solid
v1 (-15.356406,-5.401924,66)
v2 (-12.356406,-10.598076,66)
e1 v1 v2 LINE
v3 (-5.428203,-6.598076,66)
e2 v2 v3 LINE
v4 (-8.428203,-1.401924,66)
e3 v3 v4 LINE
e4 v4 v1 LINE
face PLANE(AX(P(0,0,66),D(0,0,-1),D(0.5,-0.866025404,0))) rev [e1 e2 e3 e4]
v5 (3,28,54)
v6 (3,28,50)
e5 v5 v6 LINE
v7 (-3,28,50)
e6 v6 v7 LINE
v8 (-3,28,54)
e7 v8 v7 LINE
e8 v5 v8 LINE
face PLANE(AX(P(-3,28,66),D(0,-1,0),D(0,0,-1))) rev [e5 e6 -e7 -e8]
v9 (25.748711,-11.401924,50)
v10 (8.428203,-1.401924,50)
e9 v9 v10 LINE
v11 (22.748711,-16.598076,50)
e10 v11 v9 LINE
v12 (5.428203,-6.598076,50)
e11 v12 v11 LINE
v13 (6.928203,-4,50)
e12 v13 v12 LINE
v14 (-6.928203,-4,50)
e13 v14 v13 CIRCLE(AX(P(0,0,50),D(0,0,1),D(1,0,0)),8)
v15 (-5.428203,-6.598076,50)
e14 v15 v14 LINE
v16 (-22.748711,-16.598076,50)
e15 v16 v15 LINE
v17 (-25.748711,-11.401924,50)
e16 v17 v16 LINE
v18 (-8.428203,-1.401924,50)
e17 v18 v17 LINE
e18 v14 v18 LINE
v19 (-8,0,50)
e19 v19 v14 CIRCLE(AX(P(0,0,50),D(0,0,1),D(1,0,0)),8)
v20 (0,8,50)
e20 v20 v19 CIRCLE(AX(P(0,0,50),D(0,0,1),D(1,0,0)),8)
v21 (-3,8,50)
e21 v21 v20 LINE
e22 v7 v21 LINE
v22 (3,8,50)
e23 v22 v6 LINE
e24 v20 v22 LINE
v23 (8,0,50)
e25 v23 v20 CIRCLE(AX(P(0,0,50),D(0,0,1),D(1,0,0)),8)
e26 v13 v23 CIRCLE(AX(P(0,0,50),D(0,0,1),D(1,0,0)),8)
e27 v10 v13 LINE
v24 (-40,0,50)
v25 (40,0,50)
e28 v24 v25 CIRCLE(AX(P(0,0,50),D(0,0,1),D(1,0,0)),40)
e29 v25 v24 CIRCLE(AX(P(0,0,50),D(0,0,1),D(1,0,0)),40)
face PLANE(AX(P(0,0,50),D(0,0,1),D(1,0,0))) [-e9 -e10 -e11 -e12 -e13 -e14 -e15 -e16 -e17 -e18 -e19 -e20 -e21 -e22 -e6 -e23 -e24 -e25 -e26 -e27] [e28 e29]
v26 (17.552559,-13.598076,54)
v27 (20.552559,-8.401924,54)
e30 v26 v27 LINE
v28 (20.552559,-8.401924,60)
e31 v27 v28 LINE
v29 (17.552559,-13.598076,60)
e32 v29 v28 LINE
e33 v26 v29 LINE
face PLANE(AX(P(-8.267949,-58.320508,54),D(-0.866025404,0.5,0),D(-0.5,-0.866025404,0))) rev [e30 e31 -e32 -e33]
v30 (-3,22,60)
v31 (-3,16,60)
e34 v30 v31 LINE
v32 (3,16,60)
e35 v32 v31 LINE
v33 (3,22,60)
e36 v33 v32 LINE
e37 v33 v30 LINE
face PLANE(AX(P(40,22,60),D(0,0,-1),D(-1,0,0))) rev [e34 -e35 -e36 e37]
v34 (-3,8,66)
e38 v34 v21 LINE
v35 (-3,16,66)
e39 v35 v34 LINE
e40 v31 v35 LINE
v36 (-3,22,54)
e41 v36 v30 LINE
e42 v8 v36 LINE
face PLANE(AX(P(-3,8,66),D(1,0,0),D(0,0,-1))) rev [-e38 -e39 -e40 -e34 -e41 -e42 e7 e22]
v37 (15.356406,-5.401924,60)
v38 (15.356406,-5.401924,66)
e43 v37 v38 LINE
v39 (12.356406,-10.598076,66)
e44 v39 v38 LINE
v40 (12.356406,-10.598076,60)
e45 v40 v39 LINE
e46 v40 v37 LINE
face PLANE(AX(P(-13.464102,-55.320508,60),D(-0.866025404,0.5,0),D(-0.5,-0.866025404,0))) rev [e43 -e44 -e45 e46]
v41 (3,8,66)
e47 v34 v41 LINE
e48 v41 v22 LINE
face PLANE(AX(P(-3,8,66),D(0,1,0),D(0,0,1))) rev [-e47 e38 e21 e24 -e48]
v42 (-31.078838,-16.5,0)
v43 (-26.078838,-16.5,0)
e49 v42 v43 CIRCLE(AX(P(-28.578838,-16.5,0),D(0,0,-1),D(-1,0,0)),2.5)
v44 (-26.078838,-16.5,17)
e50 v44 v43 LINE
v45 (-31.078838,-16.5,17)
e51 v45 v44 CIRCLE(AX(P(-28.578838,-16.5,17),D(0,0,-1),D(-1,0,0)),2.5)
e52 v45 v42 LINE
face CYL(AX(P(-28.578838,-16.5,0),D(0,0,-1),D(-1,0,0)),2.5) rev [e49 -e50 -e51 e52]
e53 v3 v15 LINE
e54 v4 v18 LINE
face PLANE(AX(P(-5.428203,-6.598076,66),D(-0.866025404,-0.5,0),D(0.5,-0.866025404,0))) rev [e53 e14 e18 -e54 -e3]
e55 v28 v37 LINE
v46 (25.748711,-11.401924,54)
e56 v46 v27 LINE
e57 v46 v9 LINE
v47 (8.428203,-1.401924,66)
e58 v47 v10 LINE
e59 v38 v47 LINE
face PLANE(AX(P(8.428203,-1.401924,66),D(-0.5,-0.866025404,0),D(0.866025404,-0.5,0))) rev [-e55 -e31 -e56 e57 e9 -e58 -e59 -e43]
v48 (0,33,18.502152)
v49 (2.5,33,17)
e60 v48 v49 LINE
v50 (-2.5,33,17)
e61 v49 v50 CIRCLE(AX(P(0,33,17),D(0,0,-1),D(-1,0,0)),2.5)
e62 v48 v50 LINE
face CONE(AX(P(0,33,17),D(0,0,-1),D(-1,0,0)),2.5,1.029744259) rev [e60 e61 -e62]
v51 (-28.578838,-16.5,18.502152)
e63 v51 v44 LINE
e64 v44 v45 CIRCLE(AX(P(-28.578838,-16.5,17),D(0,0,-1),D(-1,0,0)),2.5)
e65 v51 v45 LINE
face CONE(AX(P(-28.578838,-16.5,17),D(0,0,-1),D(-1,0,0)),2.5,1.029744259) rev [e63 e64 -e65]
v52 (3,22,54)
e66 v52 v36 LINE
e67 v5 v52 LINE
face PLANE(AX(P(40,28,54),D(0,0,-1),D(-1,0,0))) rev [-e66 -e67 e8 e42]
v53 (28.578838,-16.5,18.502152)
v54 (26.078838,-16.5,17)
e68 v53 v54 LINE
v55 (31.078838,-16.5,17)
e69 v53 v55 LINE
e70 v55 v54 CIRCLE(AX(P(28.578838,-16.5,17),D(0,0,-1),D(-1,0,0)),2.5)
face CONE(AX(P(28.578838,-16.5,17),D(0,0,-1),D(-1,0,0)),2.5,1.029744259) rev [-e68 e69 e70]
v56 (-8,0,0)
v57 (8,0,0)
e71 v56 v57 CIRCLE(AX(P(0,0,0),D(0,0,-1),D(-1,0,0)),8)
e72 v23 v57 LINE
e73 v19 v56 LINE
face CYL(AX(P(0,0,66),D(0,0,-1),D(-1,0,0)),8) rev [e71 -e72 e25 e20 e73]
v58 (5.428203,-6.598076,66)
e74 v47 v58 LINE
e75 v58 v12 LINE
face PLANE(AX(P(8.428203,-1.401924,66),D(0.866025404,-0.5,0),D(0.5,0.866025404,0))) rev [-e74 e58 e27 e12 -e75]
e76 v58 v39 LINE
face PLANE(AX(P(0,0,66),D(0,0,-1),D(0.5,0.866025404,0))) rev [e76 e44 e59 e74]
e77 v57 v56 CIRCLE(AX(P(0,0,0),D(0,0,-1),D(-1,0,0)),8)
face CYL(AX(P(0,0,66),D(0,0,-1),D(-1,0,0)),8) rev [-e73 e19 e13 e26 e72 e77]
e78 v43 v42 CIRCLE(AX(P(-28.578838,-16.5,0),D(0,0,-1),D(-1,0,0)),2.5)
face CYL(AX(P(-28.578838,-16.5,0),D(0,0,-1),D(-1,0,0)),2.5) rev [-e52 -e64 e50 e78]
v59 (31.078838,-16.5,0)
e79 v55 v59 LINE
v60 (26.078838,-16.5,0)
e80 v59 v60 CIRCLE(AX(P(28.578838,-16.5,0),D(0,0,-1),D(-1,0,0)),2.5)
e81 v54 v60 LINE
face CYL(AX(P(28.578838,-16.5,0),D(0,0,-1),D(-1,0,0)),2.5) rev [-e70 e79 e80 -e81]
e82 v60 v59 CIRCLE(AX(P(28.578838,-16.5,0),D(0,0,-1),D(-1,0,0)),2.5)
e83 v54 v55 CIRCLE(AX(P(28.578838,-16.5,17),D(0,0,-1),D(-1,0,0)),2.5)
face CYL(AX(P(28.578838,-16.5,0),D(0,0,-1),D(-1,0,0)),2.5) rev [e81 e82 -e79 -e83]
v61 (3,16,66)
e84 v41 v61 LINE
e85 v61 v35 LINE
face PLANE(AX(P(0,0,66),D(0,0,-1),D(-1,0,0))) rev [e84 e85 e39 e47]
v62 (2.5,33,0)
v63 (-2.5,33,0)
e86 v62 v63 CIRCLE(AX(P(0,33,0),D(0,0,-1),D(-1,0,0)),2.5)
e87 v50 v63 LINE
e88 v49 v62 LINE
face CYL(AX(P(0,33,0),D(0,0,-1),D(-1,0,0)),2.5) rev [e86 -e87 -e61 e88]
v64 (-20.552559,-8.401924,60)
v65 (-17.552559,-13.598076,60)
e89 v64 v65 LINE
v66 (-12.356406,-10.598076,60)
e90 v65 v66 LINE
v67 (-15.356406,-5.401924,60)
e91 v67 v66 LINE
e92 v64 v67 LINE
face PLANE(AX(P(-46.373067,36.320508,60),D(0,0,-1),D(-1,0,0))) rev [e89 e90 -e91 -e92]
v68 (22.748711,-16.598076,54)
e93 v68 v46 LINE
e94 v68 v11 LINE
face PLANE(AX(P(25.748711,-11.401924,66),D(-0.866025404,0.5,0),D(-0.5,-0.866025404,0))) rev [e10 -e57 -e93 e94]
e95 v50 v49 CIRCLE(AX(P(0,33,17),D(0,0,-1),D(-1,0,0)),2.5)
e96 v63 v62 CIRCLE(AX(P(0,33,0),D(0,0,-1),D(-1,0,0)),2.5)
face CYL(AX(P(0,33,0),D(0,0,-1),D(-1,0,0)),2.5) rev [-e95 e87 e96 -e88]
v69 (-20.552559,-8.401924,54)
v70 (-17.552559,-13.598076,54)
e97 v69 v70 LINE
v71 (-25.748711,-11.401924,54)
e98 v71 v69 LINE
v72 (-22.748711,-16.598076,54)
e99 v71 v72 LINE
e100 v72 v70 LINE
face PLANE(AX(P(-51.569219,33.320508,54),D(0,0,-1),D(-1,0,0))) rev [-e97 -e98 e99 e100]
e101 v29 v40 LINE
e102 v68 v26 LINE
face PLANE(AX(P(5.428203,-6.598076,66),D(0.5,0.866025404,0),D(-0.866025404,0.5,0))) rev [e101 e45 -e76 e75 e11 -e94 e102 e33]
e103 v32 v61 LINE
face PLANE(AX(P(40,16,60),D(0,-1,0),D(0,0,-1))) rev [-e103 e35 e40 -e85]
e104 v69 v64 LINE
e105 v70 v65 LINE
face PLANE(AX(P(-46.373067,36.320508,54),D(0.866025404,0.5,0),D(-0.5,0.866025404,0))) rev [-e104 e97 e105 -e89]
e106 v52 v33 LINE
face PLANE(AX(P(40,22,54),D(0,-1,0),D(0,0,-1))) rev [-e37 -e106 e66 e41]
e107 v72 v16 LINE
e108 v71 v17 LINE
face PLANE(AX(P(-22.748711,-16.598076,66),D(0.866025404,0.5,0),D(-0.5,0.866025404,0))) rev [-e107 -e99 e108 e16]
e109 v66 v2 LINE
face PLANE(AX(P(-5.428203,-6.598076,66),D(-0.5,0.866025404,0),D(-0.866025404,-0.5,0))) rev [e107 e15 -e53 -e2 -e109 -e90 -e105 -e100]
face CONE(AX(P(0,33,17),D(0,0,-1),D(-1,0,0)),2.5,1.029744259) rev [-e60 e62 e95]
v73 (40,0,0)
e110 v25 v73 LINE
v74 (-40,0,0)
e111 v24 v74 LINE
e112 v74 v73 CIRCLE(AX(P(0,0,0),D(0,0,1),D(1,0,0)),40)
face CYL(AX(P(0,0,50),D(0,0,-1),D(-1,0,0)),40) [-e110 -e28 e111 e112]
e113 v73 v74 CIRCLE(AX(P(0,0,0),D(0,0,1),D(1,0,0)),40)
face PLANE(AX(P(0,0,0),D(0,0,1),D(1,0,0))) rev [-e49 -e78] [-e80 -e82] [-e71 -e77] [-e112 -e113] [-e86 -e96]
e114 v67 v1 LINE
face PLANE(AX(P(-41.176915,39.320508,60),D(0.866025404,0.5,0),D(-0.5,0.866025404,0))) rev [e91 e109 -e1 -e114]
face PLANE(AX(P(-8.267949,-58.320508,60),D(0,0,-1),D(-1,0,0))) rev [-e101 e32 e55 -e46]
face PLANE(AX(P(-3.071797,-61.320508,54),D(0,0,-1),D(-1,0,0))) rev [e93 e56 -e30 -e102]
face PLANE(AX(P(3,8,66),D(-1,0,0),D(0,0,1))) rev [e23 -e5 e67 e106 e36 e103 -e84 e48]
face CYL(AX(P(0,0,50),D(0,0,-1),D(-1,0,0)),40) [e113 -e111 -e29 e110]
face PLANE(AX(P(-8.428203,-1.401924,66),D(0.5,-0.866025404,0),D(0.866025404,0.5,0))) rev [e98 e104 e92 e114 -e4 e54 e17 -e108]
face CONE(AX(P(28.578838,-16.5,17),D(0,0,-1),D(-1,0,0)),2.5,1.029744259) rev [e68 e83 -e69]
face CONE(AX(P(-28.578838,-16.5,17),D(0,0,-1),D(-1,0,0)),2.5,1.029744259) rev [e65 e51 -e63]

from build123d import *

# Parameters (mm, degrees)
SKETCH_1_R               = 40
EXTRUDE_1_DEPTH          = 50
SKETCH_2_W               = 6
SKETCH_2_H               = 20
EXTRUDE_2_DEPTH          = 16
CUT_EXTRUDE_1_DEPTH      = 89.345911054
PATTERN_CIRCULAR_1_COUNT = 3
SKETCH_4_R               = 8
CUT_EXTRUDE_2_DEPTH      = 87.925255248
PATTERN_CIRCULAR_2_COUNT = 3


with BuildPart() as part:
    # 草图1 → 凸台-拉伸1 (new body)
    with BuildSketch(Plane.XY):
        Circle(SKETCH_1_R)
    extrude(amount=EXTRUDE_1_DEPTH)

    # 草图2 → 凸台-拉伸2 (add)
    with BuildSketch(Plane.XY.offset(50)):
        with Locations((0, 18)):
            Rectangle(SKETCH_2_W, SKETCH_2_H)
    extrude_2 = extrude(amount=EXTRUDE_2_DEPTH)

    # 草图3 → 切除-拉伸1 (cut, through all)
    with BuildSketch(Plane.ZY.offset(3)):
        Polygon((54, 28), (54, 22), (60, 22), (60, 16), (66, 16), (66, 28), align=None)
    cut_extrude_1 = extrude(amount=-CUT_EXTRUDE_1_DEPTH, mode=Mode.SUBTRACT)

    # 阵列(圆周)1: 凸台-拉伸2, 切除-拉伸1 ×3 about axis
    pattern_circular_1_axis = Axis((0, 0, 0), (0, 0, 1))
    add([extrude_2.rotate(pattern_circular_1_axis, i * 360 / PATTERN_CIRCULAR_1_COUNT) for i in range(1, PATTERN_CIRCULAR_1_COUNT)])
    add([cut_extrude_1.rotate(pattern_circular_1_axis, i * 360 / PATTERN_CIRCULAR_1_COUNT) for i in range(1, PATTERN_CIRCULAR_1_COUNT)], mode=Mode.SUBTRACT)

    # 草图4 → 切除-拉伸2 (cut, through all)
    with BuildSketch(Plane(origin=(0, 0, 0), x_dir=(-1, 0, 0), z_dir=(0, 0, -1))):
        Circle(SKETCH_4_R)
    extrude(amount=-CUT_EXTRUDE_2_DEPTH, mode=Mode.SUBTRACT)

    # 草图5 → M6 螺纹孔1 (revolve, cut)
    with BuildSketch(Plane(origin=(0, 33, 0), x_dir=(0, 1, 0), z_dir=(1, 0, 0))):
        Polygon((0, 0), (0, 18.502151548), (2.5, 17), (2.5, 0), align=None)
    hole_wizard_m6_1 = revolve(axis=Axis((0, 33, -6.35), (0, 0, 1)), mode=Mode.SUBTRACT)

    # 阵列(圆周)2: M6 螺纹孔1 ×3 about axis
    pattern_circular_2_axis = Axis((0, 0, 0), (0, 0, 1))
    for i in range(1, PATTERN_CIRCULAR_2_COUNT):
        add(hole_wizard_m6_1.rotate(pattern_circular_2_axis, i * 360 / PATTERN_CIRCULAR_2_COUNT), mode=Mode.SUBTRACT)


solid = part.part
